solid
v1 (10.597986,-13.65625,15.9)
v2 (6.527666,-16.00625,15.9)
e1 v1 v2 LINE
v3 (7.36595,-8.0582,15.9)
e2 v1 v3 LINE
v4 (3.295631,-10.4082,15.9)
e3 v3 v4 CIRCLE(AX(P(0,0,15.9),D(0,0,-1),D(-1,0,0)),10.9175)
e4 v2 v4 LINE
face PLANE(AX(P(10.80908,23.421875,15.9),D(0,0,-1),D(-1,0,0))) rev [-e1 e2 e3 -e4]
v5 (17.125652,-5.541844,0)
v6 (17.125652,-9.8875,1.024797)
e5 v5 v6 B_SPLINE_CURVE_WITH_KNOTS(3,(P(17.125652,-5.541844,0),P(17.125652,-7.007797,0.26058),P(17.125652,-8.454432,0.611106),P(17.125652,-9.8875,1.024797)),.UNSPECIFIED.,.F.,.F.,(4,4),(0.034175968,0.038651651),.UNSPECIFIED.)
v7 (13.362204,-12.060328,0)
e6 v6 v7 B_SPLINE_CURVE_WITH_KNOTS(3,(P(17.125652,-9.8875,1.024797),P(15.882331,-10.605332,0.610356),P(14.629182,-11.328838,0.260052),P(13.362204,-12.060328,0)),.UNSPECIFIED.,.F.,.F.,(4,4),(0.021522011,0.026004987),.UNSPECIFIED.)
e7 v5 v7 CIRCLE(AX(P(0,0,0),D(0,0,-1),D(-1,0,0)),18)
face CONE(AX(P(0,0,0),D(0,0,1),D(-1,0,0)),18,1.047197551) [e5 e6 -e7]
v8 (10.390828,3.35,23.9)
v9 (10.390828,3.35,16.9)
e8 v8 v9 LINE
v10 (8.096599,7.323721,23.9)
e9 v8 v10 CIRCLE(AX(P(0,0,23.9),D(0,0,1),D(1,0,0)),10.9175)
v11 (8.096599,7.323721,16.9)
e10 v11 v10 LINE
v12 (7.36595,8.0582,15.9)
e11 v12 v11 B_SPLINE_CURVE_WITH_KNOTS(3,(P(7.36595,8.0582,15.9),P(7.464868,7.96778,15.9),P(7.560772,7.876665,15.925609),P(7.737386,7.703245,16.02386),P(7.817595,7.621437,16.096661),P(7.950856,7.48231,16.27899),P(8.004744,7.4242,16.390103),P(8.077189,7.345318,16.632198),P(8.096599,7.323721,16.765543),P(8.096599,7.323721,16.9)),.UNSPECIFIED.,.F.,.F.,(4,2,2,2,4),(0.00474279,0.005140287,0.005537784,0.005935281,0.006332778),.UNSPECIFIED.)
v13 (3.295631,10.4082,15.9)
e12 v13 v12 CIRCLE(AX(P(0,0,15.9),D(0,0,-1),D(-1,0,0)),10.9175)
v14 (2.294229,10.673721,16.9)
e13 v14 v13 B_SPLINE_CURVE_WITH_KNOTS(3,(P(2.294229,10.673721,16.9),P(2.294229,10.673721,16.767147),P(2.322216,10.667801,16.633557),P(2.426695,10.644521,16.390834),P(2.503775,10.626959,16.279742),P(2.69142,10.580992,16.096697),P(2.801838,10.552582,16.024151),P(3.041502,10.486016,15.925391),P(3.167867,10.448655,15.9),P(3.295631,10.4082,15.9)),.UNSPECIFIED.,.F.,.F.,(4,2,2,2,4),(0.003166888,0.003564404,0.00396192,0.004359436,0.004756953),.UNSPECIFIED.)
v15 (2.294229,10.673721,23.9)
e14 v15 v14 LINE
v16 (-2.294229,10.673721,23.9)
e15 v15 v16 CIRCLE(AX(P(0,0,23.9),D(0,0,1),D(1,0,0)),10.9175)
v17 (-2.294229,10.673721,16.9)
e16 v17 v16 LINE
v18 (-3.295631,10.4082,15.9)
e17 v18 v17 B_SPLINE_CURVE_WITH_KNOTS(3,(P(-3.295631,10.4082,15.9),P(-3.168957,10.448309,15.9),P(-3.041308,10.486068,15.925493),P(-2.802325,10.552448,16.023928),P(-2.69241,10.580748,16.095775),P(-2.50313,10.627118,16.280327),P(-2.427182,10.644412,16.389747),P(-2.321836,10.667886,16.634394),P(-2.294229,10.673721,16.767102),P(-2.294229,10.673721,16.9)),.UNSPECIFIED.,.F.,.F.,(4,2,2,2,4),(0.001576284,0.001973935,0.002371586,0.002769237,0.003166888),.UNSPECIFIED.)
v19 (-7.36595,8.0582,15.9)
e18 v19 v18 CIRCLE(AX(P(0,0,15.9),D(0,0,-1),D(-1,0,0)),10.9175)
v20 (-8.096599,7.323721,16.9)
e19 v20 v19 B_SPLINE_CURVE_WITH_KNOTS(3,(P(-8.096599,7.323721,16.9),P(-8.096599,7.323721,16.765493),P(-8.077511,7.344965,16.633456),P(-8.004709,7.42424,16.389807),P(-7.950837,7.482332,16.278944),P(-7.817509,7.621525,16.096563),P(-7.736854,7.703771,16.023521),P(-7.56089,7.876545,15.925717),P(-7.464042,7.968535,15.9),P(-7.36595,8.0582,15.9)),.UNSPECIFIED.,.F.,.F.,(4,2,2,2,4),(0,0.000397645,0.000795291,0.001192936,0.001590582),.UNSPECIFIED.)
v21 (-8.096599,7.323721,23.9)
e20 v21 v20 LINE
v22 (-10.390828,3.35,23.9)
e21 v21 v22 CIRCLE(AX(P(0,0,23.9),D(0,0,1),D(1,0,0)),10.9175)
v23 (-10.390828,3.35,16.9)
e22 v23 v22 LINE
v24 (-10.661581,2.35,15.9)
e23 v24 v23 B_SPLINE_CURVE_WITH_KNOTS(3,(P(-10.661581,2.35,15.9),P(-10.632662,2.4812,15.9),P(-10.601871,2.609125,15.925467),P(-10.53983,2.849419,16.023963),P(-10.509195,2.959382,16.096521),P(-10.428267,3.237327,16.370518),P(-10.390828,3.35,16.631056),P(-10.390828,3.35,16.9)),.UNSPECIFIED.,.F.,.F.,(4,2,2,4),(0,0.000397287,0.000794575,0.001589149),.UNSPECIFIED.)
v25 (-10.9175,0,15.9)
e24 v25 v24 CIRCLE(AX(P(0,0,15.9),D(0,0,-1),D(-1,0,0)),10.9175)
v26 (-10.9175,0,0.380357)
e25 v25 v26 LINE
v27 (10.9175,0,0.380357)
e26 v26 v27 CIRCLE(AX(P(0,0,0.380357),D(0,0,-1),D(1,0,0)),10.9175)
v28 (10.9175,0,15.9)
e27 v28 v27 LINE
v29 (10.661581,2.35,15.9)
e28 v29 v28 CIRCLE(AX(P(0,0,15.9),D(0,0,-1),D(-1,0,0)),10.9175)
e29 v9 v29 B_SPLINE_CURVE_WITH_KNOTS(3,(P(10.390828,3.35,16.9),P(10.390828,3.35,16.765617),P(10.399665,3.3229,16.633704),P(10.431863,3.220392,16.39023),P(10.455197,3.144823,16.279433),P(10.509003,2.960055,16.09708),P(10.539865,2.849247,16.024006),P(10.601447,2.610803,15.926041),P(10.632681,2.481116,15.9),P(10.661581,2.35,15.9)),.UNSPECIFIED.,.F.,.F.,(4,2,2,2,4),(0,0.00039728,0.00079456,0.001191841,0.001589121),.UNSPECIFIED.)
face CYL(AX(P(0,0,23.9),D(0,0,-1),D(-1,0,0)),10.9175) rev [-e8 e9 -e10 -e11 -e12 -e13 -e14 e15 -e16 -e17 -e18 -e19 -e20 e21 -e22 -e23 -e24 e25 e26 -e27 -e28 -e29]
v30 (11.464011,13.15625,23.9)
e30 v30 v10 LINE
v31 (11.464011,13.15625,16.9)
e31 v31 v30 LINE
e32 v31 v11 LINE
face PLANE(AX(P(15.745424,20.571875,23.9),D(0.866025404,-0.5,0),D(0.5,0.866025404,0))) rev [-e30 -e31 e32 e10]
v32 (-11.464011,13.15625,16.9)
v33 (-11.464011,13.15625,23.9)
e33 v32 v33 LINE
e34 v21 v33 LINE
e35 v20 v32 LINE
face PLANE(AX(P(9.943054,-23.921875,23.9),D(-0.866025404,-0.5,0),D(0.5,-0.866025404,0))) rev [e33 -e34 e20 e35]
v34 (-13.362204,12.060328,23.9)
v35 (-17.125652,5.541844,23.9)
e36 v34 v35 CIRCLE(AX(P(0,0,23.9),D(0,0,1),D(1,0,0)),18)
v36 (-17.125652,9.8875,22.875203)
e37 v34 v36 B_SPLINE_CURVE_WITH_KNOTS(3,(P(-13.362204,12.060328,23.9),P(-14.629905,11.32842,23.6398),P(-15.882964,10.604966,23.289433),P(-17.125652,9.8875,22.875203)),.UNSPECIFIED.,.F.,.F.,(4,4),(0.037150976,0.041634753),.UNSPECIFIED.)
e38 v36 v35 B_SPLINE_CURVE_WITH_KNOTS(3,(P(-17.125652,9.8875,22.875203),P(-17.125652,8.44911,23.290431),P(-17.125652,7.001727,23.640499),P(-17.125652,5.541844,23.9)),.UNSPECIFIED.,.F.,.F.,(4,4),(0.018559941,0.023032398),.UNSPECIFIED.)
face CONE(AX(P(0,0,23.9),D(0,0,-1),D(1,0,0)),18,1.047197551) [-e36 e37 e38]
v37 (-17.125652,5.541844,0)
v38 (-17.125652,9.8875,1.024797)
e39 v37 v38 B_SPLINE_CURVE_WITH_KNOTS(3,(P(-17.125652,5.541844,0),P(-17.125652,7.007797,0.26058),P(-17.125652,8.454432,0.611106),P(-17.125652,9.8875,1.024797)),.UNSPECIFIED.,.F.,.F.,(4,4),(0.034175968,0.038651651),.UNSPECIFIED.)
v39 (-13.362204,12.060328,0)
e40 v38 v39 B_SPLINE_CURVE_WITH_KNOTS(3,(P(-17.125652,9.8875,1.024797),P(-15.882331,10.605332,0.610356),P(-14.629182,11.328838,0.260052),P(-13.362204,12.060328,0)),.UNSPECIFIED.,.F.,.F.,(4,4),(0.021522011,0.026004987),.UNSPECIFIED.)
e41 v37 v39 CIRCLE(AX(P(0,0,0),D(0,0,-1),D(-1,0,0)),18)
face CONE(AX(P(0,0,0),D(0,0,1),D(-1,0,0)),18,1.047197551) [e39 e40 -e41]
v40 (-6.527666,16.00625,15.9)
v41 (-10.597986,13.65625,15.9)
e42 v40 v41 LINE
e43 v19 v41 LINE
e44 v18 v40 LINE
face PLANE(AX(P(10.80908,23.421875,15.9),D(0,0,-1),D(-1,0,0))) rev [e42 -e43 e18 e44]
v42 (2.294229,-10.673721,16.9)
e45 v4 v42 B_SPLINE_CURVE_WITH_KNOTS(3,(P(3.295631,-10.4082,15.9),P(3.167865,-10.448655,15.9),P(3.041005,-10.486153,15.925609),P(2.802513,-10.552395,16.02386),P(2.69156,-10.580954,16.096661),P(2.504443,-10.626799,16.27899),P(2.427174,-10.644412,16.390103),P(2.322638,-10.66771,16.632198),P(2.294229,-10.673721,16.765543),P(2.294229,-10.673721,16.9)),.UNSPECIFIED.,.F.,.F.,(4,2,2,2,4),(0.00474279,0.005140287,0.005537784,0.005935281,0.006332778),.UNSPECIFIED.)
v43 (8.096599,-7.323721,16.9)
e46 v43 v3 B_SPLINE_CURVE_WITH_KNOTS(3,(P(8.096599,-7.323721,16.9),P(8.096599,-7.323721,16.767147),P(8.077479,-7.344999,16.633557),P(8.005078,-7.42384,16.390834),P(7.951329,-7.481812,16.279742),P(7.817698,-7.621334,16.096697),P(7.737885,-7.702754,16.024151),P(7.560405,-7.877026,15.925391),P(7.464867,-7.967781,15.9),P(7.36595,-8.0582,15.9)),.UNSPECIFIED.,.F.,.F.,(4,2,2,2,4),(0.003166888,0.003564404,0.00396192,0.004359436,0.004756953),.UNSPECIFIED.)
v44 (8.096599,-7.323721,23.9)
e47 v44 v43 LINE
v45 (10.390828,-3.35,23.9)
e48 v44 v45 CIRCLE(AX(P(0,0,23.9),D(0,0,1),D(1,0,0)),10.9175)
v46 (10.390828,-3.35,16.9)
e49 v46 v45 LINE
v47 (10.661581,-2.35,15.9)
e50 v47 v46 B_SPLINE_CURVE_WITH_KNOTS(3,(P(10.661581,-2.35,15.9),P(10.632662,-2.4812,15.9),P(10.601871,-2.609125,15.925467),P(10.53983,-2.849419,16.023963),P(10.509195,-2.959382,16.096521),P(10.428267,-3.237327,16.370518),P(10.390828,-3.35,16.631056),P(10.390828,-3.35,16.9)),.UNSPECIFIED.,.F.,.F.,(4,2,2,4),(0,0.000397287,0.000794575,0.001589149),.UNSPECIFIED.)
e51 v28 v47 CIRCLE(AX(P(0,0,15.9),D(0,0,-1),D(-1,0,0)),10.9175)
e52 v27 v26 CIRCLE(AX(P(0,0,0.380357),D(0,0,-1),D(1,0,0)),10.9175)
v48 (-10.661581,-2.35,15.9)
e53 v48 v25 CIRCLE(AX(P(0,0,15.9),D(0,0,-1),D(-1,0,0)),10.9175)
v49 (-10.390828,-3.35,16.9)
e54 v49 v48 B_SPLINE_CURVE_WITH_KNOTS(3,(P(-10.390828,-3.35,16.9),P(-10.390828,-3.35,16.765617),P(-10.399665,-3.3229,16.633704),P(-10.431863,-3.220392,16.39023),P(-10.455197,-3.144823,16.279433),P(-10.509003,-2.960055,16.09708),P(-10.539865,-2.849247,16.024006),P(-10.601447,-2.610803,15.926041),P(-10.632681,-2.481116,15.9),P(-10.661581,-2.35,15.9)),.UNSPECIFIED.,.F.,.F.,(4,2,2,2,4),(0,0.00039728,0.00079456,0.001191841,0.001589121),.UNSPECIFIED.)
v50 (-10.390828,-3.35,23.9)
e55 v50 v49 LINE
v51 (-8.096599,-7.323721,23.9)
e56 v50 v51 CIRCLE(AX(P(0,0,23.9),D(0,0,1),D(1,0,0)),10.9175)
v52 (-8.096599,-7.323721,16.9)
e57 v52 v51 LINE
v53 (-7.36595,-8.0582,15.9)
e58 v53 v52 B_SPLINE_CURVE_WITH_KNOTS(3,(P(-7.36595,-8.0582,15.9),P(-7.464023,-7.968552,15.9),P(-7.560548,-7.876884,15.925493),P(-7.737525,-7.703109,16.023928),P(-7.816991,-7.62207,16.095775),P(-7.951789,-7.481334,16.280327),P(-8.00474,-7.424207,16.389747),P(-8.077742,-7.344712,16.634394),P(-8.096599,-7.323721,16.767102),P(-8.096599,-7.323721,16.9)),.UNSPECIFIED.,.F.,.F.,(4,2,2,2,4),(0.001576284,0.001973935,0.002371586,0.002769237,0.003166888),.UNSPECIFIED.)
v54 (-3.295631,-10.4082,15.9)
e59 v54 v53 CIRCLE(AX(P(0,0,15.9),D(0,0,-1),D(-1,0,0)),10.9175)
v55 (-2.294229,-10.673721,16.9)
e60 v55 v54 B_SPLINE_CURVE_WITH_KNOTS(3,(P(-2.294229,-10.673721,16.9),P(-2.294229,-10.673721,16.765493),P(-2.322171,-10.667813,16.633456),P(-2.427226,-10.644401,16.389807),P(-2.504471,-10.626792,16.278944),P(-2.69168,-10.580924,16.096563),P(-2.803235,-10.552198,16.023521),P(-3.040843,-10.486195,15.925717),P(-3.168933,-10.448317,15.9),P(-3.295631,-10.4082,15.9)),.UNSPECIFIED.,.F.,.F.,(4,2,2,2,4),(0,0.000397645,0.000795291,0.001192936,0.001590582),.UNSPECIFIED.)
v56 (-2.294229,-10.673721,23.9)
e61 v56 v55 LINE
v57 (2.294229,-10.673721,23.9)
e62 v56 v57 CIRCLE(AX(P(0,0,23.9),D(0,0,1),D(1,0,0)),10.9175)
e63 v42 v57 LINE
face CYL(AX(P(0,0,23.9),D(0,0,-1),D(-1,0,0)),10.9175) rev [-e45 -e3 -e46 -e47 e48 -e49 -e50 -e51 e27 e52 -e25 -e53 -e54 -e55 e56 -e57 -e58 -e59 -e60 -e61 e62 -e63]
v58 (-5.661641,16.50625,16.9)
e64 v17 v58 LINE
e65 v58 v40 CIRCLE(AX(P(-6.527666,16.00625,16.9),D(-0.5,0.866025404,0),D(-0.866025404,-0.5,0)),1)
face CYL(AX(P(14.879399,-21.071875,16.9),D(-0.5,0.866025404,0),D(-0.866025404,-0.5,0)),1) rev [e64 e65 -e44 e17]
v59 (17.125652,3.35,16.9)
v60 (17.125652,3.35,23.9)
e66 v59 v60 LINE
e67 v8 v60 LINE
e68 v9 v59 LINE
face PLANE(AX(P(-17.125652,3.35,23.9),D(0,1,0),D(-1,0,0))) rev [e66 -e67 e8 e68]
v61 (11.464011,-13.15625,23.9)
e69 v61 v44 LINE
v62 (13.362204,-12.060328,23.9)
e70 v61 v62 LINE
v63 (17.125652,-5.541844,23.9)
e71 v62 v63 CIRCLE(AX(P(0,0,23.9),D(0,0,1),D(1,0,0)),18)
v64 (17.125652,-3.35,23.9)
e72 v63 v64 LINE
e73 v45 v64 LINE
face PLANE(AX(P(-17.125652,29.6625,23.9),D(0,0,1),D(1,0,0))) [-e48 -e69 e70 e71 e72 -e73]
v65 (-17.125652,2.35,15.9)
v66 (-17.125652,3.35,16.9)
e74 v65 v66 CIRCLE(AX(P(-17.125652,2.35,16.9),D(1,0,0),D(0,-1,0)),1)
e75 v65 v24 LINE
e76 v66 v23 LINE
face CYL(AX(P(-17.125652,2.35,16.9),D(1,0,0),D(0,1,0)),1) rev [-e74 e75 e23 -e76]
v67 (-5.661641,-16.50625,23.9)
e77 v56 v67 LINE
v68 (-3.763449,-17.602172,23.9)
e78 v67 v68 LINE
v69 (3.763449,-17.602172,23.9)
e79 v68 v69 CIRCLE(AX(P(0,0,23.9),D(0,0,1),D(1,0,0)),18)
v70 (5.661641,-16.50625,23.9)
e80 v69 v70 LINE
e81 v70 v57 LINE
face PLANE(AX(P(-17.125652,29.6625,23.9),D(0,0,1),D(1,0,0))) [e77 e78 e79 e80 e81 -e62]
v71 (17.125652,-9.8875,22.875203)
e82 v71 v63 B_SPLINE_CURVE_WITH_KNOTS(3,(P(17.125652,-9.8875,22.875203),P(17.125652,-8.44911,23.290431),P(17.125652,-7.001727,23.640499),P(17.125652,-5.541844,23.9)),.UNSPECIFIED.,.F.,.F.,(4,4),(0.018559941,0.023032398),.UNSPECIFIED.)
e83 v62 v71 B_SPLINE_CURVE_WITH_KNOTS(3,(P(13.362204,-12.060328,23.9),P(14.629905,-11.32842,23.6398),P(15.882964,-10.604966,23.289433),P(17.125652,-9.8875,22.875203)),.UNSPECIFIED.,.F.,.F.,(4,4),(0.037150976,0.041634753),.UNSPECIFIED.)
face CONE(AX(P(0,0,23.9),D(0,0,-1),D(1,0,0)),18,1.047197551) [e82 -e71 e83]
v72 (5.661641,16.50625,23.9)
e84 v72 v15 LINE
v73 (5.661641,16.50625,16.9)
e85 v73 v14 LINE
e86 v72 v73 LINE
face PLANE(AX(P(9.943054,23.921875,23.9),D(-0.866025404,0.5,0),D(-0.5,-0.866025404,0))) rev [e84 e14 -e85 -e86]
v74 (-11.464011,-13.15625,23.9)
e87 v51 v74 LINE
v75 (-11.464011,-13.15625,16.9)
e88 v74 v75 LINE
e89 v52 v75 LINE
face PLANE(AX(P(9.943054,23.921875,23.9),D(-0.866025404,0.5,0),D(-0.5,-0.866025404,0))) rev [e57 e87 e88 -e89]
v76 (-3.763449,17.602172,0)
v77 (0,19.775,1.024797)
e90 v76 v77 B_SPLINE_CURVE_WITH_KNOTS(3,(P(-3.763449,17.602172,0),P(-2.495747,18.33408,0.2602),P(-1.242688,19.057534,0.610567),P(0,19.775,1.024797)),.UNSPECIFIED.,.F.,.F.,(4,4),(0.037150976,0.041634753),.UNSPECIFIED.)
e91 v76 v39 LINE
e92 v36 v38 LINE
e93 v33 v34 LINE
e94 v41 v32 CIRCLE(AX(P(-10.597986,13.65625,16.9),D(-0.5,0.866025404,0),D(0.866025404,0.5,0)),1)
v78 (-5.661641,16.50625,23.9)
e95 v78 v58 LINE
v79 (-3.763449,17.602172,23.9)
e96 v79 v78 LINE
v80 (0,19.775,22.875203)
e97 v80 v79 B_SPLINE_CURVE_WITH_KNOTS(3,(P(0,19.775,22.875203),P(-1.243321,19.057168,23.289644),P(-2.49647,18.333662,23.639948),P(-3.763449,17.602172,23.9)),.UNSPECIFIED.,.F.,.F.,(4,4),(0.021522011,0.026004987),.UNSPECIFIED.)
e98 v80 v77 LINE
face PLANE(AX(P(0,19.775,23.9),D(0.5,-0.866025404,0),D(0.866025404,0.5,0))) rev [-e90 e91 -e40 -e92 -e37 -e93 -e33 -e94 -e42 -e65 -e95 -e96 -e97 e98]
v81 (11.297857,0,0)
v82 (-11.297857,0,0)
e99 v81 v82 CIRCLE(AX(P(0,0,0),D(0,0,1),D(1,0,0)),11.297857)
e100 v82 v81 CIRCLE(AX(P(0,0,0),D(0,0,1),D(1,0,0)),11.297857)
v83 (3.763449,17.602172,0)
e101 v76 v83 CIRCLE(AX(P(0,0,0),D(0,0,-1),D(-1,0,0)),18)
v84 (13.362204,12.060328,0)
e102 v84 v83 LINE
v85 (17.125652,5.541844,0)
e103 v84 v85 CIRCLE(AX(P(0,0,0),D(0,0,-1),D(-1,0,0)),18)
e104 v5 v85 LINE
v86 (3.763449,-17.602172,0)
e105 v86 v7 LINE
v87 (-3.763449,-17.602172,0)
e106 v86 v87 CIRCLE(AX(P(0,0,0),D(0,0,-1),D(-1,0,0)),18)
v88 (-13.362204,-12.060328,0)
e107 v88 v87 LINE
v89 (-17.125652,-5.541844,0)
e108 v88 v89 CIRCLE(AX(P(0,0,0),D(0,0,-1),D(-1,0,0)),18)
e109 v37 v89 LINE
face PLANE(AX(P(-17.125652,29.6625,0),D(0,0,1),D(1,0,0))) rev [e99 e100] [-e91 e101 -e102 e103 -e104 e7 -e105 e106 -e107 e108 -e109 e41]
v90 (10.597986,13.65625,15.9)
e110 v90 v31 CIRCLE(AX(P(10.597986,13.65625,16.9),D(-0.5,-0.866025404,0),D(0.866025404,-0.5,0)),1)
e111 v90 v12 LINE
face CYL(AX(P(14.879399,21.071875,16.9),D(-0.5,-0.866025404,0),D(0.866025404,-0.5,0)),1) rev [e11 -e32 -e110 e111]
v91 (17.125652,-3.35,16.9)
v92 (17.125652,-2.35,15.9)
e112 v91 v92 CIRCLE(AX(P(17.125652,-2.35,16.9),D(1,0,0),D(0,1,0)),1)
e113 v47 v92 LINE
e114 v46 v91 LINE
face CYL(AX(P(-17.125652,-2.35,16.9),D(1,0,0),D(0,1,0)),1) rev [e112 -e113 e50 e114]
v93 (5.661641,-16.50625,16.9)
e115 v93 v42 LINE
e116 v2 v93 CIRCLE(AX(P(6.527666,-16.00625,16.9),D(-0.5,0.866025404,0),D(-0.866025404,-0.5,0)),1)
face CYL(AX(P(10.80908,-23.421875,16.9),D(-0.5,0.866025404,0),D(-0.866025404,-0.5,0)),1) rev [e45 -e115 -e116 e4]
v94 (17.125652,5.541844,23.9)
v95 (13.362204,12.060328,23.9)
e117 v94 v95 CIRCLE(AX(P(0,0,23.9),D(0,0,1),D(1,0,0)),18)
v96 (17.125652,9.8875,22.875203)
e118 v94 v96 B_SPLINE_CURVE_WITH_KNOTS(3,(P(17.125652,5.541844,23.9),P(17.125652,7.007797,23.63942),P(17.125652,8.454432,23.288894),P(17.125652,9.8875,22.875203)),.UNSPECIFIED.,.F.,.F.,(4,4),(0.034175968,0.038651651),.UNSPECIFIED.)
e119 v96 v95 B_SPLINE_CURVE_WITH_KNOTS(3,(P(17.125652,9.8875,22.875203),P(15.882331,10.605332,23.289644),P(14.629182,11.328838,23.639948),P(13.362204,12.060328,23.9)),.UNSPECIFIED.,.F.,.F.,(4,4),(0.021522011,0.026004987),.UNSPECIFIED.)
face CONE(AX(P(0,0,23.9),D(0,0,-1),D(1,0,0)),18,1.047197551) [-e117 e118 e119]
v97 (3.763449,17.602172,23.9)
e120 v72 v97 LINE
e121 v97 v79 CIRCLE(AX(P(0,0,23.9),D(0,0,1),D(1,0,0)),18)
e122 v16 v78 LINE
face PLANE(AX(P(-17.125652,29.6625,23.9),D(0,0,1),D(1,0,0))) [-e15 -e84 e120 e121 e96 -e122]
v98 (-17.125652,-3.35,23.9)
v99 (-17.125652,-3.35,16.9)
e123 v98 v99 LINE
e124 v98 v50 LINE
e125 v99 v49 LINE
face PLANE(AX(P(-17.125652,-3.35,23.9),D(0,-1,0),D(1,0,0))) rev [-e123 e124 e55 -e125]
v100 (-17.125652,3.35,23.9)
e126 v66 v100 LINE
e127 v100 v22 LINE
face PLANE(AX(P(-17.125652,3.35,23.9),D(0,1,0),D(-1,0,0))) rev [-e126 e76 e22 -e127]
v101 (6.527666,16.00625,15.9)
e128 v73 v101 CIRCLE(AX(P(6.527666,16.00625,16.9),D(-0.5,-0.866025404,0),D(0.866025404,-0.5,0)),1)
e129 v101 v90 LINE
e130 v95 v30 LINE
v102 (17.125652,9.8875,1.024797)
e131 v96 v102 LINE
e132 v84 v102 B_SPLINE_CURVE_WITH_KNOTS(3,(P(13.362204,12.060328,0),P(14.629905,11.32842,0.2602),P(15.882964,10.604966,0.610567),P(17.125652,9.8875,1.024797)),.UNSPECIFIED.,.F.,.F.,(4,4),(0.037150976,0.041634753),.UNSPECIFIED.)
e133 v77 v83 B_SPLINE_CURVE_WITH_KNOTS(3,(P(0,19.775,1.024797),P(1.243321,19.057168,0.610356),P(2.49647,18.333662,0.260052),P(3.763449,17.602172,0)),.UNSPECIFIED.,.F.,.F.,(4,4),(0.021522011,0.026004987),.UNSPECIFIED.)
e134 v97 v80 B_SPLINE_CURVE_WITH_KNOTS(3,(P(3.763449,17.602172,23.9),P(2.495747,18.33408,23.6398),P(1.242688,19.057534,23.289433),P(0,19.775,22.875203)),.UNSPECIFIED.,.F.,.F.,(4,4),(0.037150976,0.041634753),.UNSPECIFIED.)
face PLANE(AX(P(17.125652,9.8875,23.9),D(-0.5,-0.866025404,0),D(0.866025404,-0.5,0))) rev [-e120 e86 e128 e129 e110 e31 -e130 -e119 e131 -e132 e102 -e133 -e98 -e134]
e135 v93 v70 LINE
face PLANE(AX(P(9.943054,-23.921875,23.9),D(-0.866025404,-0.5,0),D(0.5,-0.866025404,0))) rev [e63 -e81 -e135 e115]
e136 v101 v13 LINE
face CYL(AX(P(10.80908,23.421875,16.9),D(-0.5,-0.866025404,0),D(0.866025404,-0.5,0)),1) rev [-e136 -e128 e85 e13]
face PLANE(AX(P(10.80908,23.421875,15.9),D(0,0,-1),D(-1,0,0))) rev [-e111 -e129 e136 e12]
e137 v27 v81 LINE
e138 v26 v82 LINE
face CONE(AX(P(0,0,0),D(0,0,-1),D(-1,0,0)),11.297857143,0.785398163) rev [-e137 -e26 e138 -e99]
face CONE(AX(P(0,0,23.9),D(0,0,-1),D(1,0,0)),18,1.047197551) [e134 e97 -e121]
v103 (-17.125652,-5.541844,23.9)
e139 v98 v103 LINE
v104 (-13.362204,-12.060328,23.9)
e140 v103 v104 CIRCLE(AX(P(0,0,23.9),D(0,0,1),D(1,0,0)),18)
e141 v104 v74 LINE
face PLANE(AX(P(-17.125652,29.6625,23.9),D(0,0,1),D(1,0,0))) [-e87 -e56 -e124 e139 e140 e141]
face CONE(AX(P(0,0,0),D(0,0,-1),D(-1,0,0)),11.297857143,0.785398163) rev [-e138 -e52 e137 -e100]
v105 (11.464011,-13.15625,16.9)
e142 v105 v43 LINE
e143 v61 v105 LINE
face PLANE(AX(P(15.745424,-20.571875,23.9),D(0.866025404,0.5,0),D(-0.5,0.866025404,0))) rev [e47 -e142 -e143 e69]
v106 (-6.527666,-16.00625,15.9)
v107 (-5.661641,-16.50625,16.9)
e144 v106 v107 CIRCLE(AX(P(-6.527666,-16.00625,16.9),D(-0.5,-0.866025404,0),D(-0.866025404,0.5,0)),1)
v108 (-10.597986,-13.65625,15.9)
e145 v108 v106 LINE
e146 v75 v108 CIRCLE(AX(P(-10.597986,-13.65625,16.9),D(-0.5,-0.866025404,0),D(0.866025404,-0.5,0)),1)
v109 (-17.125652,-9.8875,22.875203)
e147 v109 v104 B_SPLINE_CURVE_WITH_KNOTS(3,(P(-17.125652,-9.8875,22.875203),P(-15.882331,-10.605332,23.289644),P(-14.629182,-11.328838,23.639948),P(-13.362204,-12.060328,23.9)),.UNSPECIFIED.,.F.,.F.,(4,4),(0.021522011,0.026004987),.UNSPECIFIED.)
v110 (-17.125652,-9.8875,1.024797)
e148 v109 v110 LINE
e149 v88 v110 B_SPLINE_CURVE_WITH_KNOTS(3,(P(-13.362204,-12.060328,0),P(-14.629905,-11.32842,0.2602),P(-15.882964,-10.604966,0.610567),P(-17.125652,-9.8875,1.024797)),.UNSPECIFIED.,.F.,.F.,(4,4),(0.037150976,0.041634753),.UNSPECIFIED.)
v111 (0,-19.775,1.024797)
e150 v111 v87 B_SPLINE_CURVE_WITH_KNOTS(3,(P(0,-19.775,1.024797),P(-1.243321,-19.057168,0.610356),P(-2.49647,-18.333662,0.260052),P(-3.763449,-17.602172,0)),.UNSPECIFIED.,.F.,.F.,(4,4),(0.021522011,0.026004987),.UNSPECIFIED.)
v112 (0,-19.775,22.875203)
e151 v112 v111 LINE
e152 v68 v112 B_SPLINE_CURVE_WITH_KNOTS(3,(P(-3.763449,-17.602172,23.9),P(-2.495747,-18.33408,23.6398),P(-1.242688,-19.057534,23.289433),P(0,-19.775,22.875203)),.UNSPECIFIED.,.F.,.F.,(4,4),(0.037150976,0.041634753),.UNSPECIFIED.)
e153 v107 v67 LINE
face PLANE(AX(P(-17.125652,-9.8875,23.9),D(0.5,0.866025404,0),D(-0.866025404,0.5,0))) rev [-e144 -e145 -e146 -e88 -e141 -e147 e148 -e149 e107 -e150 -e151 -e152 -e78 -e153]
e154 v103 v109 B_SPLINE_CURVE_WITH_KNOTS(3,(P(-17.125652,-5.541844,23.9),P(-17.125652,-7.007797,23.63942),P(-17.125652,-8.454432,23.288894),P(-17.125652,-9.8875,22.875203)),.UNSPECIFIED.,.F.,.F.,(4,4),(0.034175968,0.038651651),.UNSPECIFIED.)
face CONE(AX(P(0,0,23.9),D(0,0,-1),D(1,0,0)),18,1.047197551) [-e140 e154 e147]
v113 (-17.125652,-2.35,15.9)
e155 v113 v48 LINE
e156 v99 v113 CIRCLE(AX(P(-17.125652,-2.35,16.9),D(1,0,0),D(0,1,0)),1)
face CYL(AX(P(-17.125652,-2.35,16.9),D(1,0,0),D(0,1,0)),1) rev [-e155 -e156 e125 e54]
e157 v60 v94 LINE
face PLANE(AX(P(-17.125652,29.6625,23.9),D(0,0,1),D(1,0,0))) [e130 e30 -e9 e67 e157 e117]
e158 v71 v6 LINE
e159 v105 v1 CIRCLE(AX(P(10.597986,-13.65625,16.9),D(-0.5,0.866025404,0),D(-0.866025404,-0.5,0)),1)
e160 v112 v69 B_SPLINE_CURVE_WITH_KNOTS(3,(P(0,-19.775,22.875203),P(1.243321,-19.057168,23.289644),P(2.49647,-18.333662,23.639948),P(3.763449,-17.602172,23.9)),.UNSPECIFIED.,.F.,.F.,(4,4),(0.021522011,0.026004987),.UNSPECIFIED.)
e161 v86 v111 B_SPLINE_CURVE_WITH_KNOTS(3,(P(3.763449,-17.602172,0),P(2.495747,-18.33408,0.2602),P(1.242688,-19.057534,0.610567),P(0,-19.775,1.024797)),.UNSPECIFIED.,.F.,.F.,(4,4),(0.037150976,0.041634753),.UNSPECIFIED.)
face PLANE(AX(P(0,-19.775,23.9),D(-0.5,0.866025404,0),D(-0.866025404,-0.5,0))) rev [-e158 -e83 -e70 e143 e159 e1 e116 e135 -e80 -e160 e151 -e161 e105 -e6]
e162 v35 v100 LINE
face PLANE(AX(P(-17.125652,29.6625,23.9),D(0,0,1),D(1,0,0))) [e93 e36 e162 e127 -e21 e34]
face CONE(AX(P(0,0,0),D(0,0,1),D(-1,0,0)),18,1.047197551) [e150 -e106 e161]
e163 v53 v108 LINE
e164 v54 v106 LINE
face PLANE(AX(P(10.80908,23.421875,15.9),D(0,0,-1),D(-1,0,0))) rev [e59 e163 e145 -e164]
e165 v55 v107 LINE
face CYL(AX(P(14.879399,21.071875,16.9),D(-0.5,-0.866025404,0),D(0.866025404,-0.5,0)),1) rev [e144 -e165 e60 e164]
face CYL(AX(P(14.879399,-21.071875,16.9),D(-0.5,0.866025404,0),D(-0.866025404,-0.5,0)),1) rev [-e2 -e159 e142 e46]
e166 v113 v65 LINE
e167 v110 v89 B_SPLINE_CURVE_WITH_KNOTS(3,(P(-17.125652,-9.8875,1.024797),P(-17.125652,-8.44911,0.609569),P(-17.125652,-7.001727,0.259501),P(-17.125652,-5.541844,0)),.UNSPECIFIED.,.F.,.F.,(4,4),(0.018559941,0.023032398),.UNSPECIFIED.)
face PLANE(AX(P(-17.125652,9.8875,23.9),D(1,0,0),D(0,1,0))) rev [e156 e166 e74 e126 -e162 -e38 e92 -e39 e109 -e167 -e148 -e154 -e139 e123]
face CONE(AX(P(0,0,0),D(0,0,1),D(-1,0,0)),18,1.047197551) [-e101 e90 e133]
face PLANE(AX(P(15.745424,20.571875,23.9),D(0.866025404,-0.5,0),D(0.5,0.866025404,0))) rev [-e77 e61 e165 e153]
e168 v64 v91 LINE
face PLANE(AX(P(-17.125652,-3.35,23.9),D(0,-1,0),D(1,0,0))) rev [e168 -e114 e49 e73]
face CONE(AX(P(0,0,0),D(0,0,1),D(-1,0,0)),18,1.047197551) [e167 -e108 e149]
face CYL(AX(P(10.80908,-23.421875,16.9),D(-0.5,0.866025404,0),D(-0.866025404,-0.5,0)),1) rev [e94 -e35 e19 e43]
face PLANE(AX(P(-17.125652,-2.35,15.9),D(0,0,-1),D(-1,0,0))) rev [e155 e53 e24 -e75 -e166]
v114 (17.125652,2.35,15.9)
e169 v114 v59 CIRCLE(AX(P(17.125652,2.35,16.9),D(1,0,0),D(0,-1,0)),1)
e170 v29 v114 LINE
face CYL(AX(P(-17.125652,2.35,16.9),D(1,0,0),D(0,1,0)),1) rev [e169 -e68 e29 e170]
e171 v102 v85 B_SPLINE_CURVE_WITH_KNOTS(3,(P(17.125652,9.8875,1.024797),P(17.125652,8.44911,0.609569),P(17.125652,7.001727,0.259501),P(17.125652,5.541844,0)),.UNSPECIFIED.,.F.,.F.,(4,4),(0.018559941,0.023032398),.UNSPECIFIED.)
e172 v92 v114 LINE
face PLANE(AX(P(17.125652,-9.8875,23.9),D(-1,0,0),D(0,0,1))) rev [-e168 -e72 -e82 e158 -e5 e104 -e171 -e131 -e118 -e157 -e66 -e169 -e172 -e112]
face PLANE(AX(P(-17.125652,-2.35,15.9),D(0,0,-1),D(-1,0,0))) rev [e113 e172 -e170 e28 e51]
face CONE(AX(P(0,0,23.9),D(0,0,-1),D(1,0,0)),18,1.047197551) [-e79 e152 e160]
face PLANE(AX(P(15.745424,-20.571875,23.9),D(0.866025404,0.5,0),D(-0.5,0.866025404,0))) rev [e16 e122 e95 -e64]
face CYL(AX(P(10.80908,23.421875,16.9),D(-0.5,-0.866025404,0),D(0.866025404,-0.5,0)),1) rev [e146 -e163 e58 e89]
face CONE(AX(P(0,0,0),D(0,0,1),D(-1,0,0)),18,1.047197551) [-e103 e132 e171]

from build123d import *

# Parameters (mm, degrees)
SKETCH_1_R               = 10.9175
EXTRUDE_814_DEPTH        = 23.9
SKETCH_2_OUTSIDE_W       = 173.966
SKETCH_2_OUTSIDE_H       = 179.264
SKETCH_2_OUTSIDE_R       = 18
CUT_EXTRUDE_1_DEPTH      = 36.433721139
CUT_EXTRUDE_1_DRAFT      = -60
SKETCH_3_OUTSIDE_W       = 173.966
SKETCH_3_OUTSIDE_H       = 179.264
SKETCH_3_OUTSIDE_R       = 18
CUT_EXTRUDE_2_DEPTH      = 36.433721139
CUT_EXTRUDE_2_DRAFT      = -60
CUT_EXTRUDE_3_DEPTH      = 47.210523693
PATTERN_CIRCULAR_1_COUNT = 3
CHAMFER_1_SIZE           = 0.380357143


with BuildPart() as part:
    # 草图1 → Extrude 814 (new body)
    with BuildSketch(Plane.XY):
        Polygon((0, 19.775), (-17.12565236, 9.8875), (-17.12565236, -9.8875), (0, -19.775), (17.12565236, -9.8875), (17.12565236, 9.8875), align=None)
        with Locations(Location((0, 0, 0), (0, 0, 180))):
            Circle(SKETCH_1_R, mode=Mode.SUBTRACT)
    extrude(amount=EXTRUDE_814_DEPTH)


with BuildPart() as cut_extrude_1_tool:
    # 草图2 outside → 切除-拉伸1 (with draft: the straight prism first)
    with BuildSketch(Plane(origin=(0, 0, 0), x_dir=(-1, 0, 0), z_dir=(0, 0, -1))):
        Rectangle(SKETCH_2_OUTSIDE_W, SKETCH_2_OUTSIDE_H)
        Circle(SKETCH_2_OUTSIDE_R, mode=Mode.SUBTRACT)
    extrude(amount=-CUT_EXTRUDE_1_DEPTH)
    # 切除-拉伸1: the draft: its side faces are tilted about the plane it starts from
    cut_extrude_1_sides = [cut_extrude_1_tool.faces().sort_by_distance(p)[0] for p in [
        (0, -89.632, 18.216860569),
        (-86.983, 0, 18.216860569),
        (0, 89.632, 18.216860569),
        (86.983, 0, 18.216860569),
        (18, 0, 18.216860569),
    ]]
    draft(cut_extrude_1_sides, Plane(origin=(0, 0, 0), x_dir=(-1, 0, 0), z_dir=(0, 0, -1)), CUT_EXTRUDE_1_DRAFT)


with BuildPart() as part_1:
    add(part.part)

    # 切除-拉伸1: cut by cut_extrude_1_tool
    add(cut_extrude_1_tool.part, mode=Mode.SUBTRACT)


with BuildPart() as cut_extrude_2_tool:
    # 草图3 outside → 切除-拉伸2 (with draft: the straight prism first)
    with BuildSketch(Plane.XY.offset(23.9)):
        Rectangle(SKETCH_3_OUTSIDE_W, SKETCH_3_OUTSIDE_H)
        Circle(SKETCH_3_OUTSIDE_R, mode=Mode.SUBTRACT)
    extrude(amount=-CUT_EXTRUDE_2_DEPTH)
    # 切除-拉伸2: the draft: its side faces are tilted about the plane it starts from
    cut_extrude_2_sides = [cut_extrude_2_tool.faces().sort_by_distance(p)[0] for p in [
        (0, -89.632, 5.683139431),
        (86.983, 0, 5.683139431),
        (0, 89.632, 5.683139431),
        (-86.983, 0, 5.683139431),
        (-18, 0, 5.683139431),
    ]]
    draft(cut_extrude_2_sides, Plane.XY.offset(23.9), CUT_EXTRUDE_2_DRAFT)


with BuildPart() as part_2:
    add(part_1.part)

    # 切除-拉伸2: cut by cut_extrude_2_tool
    add(cut_extrude_2_tool.part, mode=Mode.SUBTRACT)

    # 草图6 → 切除-拉伸3 (cut, through all)
    with BuildSketch(Plane(origin=(17.12565236, 0, 0), x_dir=(0, 0, -1), z_dir=(1, 0, 0))):
        with BuildLine():
            Line((-23.9, -3.35), (-23.9, 3.35))
            Line((-23.9, 3.35), (-16.9, 3.35))
            ThreePointArc((-16.9, 3.35), (-16.192893219, 3.057106781), (-15.9, 2.35))
            Line((-15.9, 2.35), (-15.9, -2.35))
            ThreePointArc((-15.9, -2.35), (-16.192893219, -3.057106781), (-16.9, -3.35))
            Line((-16.9, -3.35), (-23.9, -3.35))
        make_face()
    cut_extrude_3 = extrude(amount=-CUT_EXTRUDE_3_DEPTH, mode=Mode.SUBTRACT)

    # 阵列(圆周)1: 切除-拉伸3 ×3 about axis
    pattern_circular_1_axis = Axis((0, 0, 0), (0, 0, 1))
    for i in range(1, PATTERN_CIRCULAR_1_COUNT):
        add(cut_extrude_3.rotate(pattern_circular_1_axis, i * 360 / PATTERN_CIRCULAR_1_COUNT), mode=Mode.SUBTRACT)

    # 倒角1
    chamfer_1_edges = [part_2.edges().sort_by_distance(p)[0] for p in [
        (10.9175, 0, 0),
    ]]
    chamfer(chamfer_1_edges, length=CHAMFER_1_SIZE)


solid = part_2.part
